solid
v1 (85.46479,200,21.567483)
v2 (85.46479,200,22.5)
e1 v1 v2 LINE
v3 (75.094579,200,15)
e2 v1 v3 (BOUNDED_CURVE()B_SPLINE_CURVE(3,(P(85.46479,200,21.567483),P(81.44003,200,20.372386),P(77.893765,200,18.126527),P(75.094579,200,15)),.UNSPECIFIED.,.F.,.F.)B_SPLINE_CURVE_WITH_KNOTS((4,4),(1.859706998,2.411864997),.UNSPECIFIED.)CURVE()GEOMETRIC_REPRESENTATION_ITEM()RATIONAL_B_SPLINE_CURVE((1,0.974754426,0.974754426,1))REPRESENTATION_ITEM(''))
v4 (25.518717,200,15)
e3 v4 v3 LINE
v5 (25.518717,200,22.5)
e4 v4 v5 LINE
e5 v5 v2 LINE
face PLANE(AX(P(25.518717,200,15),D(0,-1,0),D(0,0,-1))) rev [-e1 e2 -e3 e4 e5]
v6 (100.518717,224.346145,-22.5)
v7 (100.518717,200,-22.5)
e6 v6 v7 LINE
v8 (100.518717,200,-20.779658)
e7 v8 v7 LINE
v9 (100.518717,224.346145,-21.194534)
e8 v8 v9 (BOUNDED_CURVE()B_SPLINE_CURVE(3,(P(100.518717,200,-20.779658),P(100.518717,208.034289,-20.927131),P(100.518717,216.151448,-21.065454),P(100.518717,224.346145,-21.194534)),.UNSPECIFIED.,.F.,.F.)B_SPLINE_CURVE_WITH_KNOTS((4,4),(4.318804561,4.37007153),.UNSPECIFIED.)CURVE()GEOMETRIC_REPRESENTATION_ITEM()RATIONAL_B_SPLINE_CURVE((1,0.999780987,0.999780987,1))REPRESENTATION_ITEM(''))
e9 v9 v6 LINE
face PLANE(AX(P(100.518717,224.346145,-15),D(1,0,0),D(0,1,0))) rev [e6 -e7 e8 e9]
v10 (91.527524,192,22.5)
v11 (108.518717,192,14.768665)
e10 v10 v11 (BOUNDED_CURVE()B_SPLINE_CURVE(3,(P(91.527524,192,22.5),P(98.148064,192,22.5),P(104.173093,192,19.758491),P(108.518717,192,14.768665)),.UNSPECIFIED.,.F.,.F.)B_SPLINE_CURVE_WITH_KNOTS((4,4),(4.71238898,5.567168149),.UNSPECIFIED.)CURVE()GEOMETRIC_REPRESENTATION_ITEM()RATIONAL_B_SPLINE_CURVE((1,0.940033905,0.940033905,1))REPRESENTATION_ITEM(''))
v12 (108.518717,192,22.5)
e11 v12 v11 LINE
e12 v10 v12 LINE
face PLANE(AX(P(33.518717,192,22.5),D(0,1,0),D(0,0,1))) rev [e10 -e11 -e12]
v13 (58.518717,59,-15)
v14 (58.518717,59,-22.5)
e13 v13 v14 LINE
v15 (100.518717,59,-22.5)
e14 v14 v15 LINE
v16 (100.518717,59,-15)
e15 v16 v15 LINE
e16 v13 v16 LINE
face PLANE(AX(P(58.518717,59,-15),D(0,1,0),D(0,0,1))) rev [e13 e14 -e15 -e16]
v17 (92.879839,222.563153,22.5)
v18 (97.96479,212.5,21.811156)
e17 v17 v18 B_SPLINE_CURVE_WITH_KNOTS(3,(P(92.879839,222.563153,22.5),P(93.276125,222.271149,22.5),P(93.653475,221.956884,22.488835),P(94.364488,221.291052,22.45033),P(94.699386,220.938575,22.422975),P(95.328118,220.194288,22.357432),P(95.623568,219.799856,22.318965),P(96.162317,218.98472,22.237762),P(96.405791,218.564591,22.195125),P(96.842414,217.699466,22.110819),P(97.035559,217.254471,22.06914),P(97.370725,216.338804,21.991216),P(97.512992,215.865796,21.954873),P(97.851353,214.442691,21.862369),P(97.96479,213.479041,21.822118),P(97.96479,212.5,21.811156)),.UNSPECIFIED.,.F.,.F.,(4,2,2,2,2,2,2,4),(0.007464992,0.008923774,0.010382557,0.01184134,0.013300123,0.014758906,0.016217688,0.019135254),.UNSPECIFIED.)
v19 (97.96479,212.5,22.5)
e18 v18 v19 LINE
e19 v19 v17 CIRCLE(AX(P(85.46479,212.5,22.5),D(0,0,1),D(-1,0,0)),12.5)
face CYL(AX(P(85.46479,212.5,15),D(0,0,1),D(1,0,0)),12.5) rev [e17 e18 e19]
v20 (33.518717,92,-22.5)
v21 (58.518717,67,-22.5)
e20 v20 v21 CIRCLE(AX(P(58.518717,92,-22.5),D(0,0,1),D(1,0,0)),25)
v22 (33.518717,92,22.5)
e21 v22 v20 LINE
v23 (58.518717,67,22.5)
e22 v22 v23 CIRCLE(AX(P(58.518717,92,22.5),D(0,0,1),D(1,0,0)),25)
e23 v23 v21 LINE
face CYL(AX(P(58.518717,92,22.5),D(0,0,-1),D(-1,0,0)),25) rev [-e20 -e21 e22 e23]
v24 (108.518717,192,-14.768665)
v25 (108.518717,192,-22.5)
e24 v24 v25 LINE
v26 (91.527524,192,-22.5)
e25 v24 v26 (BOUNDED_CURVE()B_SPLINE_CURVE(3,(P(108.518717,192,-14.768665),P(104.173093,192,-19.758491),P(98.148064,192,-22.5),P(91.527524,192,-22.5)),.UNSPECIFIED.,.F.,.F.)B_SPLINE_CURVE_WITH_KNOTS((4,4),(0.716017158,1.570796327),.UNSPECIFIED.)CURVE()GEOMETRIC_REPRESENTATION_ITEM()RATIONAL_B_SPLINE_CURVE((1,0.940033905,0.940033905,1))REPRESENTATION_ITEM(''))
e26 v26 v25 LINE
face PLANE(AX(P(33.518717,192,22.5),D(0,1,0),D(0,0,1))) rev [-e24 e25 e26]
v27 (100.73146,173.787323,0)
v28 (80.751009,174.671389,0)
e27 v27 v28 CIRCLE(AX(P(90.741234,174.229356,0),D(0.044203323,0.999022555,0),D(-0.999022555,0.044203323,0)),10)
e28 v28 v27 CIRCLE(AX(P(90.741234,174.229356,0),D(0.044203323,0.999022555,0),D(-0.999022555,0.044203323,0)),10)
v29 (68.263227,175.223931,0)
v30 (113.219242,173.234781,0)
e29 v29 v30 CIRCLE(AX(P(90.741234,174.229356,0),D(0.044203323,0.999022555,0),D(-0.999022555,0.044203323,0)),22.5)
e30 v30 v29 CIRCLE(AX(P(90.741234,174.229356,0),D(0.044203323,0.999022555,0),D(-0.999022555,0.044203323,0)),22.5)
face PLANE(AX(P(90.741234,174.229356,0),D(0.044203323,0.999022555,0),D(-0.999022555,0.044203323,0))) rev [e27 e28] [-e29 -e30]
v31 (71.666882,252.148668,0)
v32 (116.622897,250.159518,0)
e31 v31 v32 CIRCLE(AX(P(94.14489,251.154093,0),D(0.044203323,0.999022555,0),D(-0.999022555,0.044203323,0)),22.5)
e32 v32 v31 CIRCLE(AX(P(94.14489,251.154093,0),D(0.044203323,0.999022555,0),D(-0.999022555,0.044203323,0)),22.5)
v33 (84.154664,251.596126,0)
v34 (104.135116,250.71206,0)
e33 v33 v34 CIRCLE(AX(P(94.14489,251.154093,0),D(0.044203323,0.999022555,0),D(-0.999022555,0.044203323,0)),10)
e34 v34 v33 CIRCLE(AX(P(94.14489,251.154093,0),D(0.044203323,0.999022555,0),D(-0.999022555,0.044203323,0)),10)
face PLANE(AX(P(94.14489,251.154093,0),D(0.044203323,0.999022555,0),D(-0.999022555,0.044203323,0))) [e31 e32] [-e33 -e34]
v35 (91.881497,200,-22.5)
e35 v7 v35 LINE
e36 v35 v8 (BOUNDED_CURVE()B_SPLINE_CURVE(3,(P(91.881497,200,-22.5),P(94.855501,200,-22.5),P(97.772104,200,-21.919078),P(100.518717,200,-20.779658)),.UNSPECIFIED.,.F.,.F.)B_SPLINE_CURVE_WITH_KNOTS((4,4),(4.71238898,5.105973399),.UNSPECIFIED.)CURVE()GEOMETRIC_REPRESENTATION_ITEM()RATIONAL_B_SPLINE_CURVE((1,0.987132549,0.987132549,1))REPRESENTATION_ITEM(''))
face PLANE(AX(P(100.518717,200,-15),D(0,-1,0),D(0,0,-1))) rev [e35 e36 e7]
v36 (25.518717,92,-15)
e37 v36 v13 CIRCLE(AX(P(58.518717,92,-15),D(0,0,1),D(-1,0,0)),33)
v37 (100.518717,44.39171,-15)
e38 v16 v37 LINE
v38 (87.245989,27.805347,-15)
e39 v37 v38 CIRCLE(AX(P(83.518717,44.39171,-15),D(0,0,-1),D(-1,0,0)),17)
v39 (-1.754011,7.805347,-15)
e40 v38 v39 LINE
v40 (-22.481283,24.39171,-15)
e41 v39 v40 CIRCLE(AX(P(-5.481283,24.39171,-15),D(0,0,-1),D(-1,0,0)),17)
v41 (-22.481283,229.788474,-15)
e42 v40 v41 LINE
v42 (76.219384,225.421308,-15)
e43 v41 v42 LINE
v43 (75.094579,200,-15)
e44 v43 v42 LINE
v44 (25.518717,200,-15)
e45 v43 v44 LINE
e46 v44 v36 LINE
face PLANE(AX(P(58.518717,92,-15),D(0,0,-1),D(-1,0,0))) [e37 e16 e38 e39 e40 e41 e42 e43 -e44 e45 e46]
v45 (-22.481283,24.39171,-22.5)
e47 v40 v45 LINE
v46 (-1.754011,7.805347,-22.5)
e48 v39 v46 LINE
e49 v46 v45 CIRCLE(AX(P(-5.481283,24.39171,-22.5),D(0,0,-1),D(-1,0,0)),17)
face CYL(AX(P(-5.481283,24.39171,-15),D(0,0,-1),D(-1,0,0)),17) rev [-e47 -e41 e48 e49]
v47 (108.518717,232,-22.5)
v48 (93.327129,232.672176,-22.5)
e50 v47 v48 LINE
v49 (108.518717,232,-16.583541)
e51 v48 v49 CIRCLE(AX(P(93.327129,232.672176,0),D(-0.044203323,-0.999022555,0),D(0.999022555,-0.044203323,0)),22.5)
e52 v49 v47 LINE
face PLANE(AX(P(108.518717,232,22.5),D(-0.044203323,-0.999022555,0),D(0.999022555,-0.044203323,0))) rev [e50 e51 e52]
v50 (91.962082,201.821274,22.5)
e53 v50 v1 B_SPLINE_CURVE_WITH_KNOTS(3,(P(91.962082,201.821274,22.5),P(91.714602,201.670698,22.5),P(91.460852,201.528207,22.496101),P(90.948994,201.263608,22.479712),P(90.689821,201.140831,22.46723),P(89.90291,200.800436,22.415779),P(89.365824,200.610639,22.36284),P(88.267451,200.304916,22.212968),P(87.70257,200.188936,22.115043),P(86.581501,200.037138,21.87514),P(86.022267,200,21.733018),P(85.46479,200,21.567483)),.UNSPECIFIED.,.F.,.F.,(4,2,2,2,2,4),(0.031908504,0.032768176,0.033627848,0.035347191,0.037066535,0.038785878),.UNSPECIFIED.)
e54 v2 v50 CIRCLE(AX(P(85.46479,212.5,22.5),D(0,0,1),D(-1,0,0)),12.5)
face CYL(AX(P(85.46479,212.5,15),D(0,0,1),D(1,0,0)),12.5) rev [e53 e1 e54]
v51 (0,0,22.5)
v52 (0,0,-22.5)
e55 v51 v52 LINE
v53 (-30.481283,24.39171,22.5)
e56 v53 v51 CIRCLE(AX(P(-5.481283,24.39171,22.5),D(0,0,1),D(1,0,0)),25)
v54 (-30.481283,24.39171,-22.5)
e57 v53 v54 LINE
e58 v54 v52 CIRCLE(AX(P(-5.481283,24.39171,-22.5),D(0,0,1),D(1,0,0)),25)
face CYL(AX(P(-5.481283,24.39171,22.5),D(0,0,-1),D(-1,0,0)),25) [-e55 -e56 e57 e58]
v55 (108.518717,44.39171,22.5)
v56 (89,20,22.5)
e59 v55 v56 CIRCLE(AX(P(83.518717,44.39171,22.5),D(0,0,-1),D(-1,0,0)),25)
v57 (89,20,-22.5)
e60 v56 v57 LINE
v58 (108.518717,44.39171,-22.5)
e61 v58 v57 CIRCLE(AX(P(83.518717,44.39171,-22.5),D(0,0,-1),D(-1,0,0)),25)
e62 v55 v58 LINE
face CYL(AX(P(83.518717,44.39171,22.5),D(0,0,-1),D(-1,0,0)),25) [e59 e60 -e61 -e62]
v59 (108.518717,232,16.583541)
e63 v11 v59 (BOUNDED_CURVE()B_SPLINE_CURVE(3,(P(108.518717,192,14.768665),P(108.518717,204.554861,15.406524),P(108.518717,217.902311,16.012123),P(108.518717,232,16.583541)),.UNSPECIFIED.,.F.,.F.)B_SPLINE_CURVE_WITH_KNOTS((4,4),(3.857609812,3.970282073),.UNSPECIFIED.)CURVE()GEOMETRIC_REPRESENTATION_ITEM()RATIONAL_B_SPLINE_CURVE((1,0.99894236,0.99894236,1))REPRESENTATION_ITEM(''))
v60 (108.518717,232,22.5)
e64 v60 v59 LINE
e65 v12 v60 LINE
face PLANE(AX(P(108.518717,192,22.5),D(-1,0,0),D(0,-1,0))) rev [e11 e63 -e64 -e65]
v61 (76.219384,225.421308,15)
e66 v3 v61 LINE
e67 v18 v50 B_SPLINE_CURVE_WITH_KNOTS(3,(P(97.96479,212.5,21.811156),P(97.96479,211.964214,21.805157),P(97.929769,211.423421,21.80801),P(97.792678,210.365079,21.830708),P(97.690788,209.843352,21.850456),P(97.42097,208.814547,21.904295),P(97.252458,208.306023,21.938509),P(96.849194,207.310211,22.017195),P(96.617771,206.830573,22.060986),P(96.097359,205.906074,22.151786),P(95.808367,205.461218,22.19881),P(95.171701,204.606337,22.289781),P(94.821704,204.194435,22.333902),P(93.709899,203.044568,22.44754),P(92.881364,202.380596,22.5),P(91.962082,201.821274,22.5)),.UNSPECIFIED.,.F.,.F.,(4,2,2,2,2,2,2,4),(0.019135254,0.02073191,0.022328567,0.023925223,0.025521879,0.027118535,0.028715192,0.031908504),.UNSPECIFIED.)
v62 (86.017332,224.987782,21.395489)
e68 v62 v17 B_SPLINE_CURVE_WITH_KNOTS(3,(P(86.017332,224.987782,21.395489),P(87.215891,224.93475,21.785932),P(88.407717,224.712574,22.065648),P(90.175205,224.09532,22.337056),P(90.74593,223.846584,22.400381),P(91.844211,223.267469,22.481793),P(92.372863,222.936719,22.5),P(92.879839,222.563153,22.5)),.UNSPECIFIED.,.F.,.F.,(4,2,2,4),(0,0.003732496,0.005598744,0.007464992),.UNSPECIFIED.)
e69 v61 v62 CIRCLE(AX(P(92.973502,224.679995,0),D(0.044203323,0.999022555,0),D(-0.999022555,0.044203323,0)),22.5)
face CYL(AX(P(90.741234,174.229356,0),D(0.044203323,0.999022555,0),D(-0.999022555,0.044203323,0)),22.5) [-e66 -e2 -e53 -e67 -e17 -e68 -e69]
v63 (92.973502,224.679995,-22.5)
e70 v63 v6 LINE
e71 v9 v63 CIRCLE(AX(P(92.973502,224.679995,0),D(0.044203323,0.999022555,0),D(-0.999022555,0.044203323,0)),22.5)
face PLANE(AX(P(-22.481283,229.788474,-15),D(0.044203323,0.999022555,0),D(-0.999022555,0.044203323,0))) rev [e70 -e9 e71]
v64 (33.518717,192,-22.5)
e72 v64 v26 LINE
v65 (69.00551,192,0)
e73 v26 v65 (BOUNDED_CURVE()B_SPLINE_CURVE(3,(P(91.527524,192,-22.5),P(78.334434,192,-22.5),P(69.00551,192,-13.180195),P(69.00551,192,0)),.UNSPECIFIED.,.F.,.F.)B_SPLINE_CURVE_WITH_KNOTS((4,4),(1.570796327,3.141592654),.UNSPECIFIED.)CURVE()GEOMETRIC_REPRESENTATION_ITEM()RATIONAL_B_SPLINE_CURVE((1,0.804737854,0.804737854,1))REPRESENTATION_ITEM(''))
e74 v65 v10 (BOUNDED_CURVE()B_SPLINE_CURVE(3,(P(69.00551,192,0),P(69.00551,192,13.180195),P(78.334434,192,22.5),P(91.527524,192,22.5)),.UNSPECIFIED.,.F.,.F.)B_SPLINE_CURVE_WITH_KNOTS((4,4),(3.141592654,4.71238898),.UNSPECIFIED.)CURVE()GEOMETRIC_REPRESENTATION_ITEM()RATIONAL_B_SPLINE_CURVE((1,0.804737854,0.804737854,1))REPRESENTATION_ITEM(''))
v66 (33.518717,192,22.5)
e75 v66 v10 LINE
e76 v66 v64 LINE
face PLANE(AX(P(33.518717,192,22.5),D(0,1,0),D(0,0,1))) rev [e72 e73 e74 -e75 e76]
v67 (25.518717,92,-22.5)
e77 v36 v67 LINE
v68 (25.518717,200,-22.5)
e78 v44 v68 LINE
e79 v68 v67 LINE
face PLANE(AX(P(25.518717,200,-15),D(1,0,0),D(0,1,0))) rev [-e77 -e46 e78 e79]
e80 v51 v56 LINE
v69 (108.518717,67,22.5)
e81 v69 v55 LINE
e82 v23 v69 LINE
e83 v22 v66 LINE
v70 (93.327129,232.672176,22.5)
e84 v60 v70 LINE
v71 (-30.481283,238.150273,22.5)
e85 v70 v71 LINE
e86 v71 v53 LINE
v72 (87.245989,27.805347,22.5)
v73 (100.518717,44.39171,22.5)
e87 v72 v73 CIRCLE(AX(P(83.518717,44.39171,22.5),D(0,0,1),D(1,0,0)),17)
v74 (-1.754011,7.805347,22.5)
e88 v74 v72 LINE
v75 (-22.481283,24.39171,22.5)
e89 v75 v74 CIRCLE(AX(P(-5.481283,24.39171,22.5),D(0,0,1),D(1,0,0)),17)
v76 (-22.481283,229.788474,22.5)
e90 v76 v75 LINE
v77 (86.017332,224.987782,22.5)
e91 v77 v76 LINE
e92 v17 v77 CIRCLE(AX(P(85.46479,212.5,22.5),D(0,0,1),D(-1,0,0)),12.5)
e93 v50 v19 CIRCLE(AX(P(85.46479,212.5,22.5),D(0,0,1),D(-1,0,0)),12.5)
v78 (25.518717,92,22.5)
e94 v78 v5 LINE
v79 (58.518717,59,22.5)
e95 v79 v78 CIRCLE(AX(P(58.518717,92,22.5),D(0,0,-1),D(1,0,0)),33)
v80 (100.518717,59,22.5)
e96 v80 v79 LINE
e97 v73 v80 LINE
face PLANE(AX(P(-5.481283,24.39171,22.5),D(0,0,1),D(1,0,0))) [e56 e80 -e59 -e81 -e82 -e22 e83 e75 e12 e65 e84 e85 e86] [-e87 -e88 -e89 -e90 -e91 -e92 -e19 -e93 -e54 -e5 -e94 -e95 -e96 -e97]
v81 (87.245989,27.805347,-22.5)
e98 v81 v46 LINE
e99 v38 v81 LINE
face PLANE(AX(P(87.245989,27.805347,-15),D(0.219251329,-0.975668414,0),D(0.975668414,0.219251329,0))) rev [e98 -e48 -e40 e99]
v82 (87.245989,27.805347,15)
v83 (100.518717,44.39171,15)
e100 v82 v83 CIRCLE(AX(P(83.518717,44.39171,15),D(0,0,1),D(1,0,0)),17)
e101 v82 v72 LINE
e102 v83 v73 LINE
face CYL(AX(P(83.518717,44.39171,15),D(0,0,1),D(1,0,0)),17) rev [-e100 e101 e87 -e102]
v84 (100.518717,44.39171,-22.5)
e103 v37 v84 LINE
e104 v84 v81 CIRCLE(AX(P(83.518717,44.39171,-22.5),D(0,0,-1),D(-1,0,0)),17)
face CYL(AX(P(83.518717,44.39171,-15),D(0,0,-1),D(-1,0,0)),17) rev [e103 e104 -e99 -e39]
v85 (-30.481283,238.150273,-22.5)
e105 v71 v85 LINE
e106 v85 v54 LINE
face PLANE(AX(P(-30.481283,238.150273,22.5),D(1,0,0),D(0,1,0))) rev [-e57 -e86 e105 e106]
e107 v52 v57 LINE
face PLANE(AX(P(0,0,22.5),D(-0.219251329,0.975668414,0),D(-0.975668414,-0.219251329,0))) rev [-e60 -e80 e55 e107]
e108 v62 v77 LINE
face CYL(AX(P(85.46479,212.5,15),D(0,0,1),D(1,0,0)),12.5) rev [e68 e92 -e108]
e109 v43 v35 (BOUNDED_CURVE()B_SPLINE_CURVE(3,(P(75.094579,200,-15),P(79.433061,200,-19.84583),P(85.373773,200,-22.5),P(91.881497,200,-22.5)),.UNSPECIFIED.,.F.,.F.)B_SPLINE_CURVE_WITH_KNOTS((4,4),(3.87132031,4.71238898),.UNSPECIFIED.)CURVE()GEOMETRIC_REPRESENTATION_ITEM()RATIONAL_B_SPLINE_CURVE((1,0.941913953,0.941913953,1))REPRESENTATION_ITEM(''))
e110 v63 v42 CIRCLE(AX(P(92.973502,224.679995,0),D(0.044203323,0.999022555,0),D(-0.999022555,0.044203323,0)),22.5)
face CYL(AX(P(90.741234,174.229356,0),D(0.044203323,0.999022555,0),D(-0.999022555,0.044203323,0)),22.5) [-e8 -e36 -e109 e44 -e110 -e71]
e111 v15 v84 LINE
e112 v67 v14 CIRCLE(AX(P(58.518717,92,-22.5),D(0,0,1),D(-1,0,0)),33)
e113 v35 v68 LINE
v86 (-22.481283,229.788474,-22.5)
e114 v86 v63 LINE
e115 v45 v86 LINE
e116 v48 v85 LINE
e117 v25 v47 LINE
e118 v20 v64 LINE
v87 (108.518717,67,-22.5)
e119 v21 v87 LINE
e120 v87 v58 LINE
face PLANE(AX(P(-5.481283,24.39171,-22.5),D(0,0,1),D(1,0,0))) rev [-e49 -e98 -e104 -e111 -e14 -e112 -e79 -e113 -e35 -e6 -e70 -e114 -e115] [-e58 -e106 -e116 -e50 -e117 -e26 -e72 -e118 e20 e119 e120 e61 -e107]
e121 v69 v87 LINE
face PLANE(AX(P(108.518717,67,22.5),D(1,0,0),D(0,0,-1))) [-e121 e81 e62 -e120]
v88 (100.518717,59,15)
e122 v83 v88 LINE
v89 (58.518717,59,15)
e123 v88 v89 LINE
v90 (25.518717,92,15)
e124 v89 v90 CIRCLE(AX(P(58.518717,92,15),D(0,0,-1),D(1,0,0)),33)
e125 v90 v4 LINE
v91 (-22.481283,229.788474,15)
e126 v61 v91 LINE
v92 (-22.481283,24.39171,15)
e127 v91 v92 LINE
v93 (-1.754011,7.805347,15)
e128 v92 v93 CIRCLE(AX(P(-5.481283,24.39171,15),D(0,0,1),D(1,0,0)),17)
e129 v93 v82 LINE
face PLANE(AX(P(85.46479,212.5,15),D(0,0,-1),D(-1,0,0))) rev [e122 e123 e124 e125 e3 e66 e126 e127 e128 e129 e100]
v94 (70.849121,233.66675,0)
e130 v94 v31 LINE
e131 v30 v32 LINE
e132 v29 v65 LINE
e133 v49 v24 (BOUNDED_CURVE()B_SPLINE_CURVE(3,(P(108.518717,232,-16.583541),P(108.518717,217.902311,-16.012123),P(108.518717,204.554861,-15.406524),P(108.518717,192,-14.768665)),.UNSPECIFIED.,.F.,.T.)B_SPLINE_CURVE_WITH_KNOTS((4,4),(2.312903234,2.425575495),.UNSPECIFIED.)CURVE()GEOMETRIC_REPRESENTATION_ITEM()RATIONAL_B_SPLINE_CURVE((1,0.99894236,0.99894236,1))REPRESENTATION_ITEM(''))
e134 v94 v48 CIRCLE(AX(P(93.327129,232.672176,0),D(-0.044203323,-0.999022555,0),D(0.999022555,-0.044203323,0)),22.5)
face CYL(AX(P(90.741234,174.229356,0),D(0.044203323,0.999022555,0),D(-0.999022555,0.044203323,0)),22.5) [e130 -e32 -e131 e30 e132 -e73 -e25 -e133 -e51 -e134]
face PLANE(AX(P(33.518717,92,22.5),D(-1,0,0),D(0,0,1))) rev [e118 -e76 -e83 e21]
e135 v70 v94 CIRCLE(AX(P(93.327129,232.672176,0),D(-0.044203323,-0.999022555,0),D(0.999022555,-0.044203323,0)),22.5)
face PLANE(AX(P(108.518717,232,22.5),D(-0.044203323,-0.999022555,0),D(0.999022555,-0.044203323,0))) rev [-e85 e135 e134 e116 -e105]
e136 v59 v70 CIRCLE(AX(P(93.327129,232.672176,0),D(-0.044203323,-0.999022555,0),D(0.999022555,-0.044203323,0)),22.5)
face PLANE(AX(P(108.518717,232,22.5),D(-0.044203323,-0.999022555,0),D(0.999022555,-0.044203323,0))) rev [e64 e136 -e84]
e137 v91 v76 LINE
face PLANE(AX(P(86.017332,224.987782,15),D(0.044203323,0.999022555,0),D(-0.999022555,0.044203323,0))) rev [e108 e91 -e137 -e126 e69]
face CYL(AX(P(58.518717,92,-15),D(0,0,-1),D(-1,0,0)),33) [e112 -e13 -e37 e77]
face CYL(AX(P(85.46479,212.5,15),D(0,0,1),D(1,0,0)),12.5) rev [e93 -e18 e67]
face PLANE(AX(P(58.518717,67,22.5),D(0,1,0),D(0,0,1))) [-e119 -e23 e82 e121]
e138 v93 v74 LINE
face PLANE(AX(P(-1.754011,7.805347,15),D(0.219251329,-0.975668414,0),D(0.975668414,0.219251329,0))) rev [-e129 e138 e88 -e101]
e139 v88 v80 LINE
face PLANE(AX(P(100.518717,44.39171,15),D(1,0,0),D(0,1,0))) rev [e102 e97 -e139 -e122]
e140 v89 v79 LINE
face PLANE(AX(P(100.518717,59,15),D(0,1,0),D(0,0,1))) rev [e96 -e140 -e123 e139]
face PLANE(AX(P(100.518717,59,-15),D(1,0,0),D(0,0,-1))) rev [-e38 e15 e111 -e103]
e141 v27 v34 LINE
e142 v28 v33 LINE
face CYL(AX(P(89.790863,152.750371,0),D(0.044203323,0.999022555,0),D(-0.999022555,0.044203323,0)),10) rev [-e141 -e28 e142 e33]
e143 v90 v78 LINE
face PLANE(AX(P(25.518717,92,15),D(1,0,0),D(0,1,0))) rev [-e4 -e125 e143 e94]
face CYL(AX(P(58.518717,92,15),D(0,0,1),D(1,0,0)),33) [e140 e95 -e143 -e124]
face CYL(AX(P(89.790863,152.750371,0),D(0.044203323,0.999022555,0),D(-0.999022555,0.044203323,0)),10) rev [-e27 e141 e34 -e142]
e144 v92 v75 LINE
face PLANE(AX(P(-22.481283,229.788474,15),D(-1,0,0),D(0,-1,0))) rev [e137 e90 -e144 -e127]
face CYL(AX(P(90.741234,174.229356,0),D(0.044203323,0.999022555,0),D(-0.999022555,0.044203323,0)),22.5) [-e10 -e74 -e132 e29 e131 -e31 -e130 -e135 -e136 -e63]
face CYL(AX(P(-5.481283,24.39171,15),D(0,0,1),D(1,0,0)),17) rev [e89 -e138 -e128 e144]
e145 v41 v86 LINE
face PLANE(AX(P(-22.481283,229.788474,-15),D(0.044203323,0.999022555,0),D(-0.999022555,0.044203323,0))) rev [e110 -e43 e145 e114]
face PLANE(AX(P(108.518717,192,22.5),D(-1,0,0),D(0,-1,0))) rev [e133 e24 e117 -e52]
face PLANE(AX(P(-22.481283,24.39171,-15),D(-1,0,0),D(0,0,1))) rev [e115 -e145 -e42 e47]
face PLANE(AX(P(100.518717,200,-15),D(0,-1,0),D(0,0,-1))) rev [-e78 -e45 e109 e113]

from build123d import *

# Parameters (mm, degrees)
C_FRAME_DEPTH         = 22.5
FRONT_POCKET_DEPTH    = 7.5
BACK_START            = -7.5
BACK_POCKET_DEPTH     = 7.5
SCREW_BOSS_DEPTH      = 18.5
SCREW_BOSS_DEPTH_BACK = 58.5
SCREW_BOSS_SKETCH_R   = 22.5
SCREW_HOLE_SKETCH_R   = 10
SCREW_HOLE_DEPTH      = 98.5


with BuildPart() as part:
    # C Frame Profile Sketch → C Frame (new, symmetric)
    with BuildSketch(Plane.XY):
        with BuildLine():
            Line((108.518716773, 232), (-30.481283227, 238.150273432))
            Line((-30.481283227, 238.150273432), (-30.481283227, 24.391710358))
            ThreePointArc((-30.481283227, 24.391710358), (-21.101269131, 4.872078181), (0, 0))
            Line((0, 0), (89, 20))
            ThreePointArc((89, 20), (103.038348951, 28.771724453), (108.518716773, 44.391710358))
            Line((108.518716773, 44.391710358), (108.518716773, 67))
            Line((108.518716773, 67), (58.518716773, 67))
            ThreePointArc((58.518716773, 67), (40.841047244, 74.32233047), (33.518716773, 92))
            Line((33.518716773, 92), (33.518716773, 192))
            Line((33.518716773, 192), (108.518716773, 192))
            Line((108.518716773, 192), (108.518716773, 232))
        make_face()
    extrude(amount=C_FRAME_DEPTH, both=True)

    # Front Pocket Sketch → Front Pocket (cut)
    with BuildSketch(Plane.XY.offset(22.5)):
        with BuildLine():
            Line((-22.481283227, 229.788473653), (-22.481283227, 24.391710358))
            ThreePointArc((-22.481283227, 24.391710358), (-16.102873642, 11.118360478), (-1.754010632, 7.805347315))
            Line((-1.754010632, 7.805347315), (87.245989368, 27.805347315))
            ThreePointArc((87.245989368, 27.805347315), (96.792066654, 33.770119943), (100.518716773, 44.391710358))
            Line((100.518716773, 44.391710358), (100.518716773, 59))
            Line((100.518716773, 59), (58.518716773, 59))
            ThreePointArc((58.518716773, 59), (35.184192994, 68.665476221), (25.518716773, 92))
            Line((25.518716773, 92), (25.518716773, 200))
            Line((25.518716773, 200), (85.464789993, 200))
            ThreePointArc((85.464789993, 200), (97.961735105, 212.223661697), (86.017331529, 224.987781943))
            Line((86.017331529, 224.987781943), (-22.481283227, 229.788473653))
        make_face()
    extrude(amount=-FRONT_POCKET_DEPTH, mode=Mode.SUBTRACT)

    # Back Pocket Sketch → Back Pocket (cut)
    with BuildSketch(Plane(origin=(0, 0, -22.5), x_dir=(-1, 0, 0), z_dir=(0, 0, -1)).offset(BACK_START)):
        with BuildLine():
            Line((-58.518716773, 59), (-100.518716773, 59))
            Line((-100.518716773, 59), (-100.518716773, 44.391710358))
            ThreePointArc((-100.518716773, 44.391710358), (-96.792066654, 33.770119943), (-87.245989368, 27.805347315))
            Line((-87.245989368, 27.805347315), (1.754010632, 7.805347315))
            ThreePointArc((1.754010632, 7.805347315), (16.102873642, 11.118360478), (22.481283227, 24.391710358))
            Line((22.481283227, 24.391710358), (22.481283227, 229.788473653))
            Line((22.481283227, 229.788473653), (-100.518716773, 224.346145364))
            Line((-100.518716773, 224.346145364), (-100.518716773, 200))
            Line((-100.518716773, 200), (-25.518716773, 200))
            Line((-25.518716773, 200), (-25.518716773, 92))
            ThreePointArc((-25.518716773, 92), (-35.184192994, 68.665476221), (-58.518716773, 59))
        make_face()
    extrude(amount=BACK_POCKET_DEPTH, mode=Mode.SUBTRACT)

    # Screw Boss Sketch → Screw Boss (add, two sides: drawn at the far end of the back side and taken through both)
    with BuildSketch(Plane(origin=(10.457185431, 236.338886554, 0), x_dir=(0.9990225554240701, -0.0442033228837011, 0), z_dir=(0.0442033228837011, 0.9990225554240703, 0)).offset(-SCREW_BOSS_DEPTH_BACK)):
        with Locations(Location((82.951023109, 0, 0), (0, 0, 180))):
            Circle(SCREW_BOSS_SKETCH_R)
    extrude(amount=SCREW_BOSS_DEPTH + SCREW_BOSS_DEPTH_BACK)

    # Screw Hole Sketch → Screw Hole (cut)
    with BuildSketch(Plane(origin=(11.274946905, 254.820803829, 0), x_dir=(0.9990225554240701, -0.04420332288370111, 0), z_dir=(0.04420332288370111, 0.9990225554240703, 0))):
        with Locations(Location((82.951023109, 0, 0), (0, 0, 180))):
            Circle(SCREW_HOLE_SKETCH_R)
    extrude(amount=-SCREW_HOLE_DEPTH, mode=Mode.SUBTRACT)


solid = part.part
